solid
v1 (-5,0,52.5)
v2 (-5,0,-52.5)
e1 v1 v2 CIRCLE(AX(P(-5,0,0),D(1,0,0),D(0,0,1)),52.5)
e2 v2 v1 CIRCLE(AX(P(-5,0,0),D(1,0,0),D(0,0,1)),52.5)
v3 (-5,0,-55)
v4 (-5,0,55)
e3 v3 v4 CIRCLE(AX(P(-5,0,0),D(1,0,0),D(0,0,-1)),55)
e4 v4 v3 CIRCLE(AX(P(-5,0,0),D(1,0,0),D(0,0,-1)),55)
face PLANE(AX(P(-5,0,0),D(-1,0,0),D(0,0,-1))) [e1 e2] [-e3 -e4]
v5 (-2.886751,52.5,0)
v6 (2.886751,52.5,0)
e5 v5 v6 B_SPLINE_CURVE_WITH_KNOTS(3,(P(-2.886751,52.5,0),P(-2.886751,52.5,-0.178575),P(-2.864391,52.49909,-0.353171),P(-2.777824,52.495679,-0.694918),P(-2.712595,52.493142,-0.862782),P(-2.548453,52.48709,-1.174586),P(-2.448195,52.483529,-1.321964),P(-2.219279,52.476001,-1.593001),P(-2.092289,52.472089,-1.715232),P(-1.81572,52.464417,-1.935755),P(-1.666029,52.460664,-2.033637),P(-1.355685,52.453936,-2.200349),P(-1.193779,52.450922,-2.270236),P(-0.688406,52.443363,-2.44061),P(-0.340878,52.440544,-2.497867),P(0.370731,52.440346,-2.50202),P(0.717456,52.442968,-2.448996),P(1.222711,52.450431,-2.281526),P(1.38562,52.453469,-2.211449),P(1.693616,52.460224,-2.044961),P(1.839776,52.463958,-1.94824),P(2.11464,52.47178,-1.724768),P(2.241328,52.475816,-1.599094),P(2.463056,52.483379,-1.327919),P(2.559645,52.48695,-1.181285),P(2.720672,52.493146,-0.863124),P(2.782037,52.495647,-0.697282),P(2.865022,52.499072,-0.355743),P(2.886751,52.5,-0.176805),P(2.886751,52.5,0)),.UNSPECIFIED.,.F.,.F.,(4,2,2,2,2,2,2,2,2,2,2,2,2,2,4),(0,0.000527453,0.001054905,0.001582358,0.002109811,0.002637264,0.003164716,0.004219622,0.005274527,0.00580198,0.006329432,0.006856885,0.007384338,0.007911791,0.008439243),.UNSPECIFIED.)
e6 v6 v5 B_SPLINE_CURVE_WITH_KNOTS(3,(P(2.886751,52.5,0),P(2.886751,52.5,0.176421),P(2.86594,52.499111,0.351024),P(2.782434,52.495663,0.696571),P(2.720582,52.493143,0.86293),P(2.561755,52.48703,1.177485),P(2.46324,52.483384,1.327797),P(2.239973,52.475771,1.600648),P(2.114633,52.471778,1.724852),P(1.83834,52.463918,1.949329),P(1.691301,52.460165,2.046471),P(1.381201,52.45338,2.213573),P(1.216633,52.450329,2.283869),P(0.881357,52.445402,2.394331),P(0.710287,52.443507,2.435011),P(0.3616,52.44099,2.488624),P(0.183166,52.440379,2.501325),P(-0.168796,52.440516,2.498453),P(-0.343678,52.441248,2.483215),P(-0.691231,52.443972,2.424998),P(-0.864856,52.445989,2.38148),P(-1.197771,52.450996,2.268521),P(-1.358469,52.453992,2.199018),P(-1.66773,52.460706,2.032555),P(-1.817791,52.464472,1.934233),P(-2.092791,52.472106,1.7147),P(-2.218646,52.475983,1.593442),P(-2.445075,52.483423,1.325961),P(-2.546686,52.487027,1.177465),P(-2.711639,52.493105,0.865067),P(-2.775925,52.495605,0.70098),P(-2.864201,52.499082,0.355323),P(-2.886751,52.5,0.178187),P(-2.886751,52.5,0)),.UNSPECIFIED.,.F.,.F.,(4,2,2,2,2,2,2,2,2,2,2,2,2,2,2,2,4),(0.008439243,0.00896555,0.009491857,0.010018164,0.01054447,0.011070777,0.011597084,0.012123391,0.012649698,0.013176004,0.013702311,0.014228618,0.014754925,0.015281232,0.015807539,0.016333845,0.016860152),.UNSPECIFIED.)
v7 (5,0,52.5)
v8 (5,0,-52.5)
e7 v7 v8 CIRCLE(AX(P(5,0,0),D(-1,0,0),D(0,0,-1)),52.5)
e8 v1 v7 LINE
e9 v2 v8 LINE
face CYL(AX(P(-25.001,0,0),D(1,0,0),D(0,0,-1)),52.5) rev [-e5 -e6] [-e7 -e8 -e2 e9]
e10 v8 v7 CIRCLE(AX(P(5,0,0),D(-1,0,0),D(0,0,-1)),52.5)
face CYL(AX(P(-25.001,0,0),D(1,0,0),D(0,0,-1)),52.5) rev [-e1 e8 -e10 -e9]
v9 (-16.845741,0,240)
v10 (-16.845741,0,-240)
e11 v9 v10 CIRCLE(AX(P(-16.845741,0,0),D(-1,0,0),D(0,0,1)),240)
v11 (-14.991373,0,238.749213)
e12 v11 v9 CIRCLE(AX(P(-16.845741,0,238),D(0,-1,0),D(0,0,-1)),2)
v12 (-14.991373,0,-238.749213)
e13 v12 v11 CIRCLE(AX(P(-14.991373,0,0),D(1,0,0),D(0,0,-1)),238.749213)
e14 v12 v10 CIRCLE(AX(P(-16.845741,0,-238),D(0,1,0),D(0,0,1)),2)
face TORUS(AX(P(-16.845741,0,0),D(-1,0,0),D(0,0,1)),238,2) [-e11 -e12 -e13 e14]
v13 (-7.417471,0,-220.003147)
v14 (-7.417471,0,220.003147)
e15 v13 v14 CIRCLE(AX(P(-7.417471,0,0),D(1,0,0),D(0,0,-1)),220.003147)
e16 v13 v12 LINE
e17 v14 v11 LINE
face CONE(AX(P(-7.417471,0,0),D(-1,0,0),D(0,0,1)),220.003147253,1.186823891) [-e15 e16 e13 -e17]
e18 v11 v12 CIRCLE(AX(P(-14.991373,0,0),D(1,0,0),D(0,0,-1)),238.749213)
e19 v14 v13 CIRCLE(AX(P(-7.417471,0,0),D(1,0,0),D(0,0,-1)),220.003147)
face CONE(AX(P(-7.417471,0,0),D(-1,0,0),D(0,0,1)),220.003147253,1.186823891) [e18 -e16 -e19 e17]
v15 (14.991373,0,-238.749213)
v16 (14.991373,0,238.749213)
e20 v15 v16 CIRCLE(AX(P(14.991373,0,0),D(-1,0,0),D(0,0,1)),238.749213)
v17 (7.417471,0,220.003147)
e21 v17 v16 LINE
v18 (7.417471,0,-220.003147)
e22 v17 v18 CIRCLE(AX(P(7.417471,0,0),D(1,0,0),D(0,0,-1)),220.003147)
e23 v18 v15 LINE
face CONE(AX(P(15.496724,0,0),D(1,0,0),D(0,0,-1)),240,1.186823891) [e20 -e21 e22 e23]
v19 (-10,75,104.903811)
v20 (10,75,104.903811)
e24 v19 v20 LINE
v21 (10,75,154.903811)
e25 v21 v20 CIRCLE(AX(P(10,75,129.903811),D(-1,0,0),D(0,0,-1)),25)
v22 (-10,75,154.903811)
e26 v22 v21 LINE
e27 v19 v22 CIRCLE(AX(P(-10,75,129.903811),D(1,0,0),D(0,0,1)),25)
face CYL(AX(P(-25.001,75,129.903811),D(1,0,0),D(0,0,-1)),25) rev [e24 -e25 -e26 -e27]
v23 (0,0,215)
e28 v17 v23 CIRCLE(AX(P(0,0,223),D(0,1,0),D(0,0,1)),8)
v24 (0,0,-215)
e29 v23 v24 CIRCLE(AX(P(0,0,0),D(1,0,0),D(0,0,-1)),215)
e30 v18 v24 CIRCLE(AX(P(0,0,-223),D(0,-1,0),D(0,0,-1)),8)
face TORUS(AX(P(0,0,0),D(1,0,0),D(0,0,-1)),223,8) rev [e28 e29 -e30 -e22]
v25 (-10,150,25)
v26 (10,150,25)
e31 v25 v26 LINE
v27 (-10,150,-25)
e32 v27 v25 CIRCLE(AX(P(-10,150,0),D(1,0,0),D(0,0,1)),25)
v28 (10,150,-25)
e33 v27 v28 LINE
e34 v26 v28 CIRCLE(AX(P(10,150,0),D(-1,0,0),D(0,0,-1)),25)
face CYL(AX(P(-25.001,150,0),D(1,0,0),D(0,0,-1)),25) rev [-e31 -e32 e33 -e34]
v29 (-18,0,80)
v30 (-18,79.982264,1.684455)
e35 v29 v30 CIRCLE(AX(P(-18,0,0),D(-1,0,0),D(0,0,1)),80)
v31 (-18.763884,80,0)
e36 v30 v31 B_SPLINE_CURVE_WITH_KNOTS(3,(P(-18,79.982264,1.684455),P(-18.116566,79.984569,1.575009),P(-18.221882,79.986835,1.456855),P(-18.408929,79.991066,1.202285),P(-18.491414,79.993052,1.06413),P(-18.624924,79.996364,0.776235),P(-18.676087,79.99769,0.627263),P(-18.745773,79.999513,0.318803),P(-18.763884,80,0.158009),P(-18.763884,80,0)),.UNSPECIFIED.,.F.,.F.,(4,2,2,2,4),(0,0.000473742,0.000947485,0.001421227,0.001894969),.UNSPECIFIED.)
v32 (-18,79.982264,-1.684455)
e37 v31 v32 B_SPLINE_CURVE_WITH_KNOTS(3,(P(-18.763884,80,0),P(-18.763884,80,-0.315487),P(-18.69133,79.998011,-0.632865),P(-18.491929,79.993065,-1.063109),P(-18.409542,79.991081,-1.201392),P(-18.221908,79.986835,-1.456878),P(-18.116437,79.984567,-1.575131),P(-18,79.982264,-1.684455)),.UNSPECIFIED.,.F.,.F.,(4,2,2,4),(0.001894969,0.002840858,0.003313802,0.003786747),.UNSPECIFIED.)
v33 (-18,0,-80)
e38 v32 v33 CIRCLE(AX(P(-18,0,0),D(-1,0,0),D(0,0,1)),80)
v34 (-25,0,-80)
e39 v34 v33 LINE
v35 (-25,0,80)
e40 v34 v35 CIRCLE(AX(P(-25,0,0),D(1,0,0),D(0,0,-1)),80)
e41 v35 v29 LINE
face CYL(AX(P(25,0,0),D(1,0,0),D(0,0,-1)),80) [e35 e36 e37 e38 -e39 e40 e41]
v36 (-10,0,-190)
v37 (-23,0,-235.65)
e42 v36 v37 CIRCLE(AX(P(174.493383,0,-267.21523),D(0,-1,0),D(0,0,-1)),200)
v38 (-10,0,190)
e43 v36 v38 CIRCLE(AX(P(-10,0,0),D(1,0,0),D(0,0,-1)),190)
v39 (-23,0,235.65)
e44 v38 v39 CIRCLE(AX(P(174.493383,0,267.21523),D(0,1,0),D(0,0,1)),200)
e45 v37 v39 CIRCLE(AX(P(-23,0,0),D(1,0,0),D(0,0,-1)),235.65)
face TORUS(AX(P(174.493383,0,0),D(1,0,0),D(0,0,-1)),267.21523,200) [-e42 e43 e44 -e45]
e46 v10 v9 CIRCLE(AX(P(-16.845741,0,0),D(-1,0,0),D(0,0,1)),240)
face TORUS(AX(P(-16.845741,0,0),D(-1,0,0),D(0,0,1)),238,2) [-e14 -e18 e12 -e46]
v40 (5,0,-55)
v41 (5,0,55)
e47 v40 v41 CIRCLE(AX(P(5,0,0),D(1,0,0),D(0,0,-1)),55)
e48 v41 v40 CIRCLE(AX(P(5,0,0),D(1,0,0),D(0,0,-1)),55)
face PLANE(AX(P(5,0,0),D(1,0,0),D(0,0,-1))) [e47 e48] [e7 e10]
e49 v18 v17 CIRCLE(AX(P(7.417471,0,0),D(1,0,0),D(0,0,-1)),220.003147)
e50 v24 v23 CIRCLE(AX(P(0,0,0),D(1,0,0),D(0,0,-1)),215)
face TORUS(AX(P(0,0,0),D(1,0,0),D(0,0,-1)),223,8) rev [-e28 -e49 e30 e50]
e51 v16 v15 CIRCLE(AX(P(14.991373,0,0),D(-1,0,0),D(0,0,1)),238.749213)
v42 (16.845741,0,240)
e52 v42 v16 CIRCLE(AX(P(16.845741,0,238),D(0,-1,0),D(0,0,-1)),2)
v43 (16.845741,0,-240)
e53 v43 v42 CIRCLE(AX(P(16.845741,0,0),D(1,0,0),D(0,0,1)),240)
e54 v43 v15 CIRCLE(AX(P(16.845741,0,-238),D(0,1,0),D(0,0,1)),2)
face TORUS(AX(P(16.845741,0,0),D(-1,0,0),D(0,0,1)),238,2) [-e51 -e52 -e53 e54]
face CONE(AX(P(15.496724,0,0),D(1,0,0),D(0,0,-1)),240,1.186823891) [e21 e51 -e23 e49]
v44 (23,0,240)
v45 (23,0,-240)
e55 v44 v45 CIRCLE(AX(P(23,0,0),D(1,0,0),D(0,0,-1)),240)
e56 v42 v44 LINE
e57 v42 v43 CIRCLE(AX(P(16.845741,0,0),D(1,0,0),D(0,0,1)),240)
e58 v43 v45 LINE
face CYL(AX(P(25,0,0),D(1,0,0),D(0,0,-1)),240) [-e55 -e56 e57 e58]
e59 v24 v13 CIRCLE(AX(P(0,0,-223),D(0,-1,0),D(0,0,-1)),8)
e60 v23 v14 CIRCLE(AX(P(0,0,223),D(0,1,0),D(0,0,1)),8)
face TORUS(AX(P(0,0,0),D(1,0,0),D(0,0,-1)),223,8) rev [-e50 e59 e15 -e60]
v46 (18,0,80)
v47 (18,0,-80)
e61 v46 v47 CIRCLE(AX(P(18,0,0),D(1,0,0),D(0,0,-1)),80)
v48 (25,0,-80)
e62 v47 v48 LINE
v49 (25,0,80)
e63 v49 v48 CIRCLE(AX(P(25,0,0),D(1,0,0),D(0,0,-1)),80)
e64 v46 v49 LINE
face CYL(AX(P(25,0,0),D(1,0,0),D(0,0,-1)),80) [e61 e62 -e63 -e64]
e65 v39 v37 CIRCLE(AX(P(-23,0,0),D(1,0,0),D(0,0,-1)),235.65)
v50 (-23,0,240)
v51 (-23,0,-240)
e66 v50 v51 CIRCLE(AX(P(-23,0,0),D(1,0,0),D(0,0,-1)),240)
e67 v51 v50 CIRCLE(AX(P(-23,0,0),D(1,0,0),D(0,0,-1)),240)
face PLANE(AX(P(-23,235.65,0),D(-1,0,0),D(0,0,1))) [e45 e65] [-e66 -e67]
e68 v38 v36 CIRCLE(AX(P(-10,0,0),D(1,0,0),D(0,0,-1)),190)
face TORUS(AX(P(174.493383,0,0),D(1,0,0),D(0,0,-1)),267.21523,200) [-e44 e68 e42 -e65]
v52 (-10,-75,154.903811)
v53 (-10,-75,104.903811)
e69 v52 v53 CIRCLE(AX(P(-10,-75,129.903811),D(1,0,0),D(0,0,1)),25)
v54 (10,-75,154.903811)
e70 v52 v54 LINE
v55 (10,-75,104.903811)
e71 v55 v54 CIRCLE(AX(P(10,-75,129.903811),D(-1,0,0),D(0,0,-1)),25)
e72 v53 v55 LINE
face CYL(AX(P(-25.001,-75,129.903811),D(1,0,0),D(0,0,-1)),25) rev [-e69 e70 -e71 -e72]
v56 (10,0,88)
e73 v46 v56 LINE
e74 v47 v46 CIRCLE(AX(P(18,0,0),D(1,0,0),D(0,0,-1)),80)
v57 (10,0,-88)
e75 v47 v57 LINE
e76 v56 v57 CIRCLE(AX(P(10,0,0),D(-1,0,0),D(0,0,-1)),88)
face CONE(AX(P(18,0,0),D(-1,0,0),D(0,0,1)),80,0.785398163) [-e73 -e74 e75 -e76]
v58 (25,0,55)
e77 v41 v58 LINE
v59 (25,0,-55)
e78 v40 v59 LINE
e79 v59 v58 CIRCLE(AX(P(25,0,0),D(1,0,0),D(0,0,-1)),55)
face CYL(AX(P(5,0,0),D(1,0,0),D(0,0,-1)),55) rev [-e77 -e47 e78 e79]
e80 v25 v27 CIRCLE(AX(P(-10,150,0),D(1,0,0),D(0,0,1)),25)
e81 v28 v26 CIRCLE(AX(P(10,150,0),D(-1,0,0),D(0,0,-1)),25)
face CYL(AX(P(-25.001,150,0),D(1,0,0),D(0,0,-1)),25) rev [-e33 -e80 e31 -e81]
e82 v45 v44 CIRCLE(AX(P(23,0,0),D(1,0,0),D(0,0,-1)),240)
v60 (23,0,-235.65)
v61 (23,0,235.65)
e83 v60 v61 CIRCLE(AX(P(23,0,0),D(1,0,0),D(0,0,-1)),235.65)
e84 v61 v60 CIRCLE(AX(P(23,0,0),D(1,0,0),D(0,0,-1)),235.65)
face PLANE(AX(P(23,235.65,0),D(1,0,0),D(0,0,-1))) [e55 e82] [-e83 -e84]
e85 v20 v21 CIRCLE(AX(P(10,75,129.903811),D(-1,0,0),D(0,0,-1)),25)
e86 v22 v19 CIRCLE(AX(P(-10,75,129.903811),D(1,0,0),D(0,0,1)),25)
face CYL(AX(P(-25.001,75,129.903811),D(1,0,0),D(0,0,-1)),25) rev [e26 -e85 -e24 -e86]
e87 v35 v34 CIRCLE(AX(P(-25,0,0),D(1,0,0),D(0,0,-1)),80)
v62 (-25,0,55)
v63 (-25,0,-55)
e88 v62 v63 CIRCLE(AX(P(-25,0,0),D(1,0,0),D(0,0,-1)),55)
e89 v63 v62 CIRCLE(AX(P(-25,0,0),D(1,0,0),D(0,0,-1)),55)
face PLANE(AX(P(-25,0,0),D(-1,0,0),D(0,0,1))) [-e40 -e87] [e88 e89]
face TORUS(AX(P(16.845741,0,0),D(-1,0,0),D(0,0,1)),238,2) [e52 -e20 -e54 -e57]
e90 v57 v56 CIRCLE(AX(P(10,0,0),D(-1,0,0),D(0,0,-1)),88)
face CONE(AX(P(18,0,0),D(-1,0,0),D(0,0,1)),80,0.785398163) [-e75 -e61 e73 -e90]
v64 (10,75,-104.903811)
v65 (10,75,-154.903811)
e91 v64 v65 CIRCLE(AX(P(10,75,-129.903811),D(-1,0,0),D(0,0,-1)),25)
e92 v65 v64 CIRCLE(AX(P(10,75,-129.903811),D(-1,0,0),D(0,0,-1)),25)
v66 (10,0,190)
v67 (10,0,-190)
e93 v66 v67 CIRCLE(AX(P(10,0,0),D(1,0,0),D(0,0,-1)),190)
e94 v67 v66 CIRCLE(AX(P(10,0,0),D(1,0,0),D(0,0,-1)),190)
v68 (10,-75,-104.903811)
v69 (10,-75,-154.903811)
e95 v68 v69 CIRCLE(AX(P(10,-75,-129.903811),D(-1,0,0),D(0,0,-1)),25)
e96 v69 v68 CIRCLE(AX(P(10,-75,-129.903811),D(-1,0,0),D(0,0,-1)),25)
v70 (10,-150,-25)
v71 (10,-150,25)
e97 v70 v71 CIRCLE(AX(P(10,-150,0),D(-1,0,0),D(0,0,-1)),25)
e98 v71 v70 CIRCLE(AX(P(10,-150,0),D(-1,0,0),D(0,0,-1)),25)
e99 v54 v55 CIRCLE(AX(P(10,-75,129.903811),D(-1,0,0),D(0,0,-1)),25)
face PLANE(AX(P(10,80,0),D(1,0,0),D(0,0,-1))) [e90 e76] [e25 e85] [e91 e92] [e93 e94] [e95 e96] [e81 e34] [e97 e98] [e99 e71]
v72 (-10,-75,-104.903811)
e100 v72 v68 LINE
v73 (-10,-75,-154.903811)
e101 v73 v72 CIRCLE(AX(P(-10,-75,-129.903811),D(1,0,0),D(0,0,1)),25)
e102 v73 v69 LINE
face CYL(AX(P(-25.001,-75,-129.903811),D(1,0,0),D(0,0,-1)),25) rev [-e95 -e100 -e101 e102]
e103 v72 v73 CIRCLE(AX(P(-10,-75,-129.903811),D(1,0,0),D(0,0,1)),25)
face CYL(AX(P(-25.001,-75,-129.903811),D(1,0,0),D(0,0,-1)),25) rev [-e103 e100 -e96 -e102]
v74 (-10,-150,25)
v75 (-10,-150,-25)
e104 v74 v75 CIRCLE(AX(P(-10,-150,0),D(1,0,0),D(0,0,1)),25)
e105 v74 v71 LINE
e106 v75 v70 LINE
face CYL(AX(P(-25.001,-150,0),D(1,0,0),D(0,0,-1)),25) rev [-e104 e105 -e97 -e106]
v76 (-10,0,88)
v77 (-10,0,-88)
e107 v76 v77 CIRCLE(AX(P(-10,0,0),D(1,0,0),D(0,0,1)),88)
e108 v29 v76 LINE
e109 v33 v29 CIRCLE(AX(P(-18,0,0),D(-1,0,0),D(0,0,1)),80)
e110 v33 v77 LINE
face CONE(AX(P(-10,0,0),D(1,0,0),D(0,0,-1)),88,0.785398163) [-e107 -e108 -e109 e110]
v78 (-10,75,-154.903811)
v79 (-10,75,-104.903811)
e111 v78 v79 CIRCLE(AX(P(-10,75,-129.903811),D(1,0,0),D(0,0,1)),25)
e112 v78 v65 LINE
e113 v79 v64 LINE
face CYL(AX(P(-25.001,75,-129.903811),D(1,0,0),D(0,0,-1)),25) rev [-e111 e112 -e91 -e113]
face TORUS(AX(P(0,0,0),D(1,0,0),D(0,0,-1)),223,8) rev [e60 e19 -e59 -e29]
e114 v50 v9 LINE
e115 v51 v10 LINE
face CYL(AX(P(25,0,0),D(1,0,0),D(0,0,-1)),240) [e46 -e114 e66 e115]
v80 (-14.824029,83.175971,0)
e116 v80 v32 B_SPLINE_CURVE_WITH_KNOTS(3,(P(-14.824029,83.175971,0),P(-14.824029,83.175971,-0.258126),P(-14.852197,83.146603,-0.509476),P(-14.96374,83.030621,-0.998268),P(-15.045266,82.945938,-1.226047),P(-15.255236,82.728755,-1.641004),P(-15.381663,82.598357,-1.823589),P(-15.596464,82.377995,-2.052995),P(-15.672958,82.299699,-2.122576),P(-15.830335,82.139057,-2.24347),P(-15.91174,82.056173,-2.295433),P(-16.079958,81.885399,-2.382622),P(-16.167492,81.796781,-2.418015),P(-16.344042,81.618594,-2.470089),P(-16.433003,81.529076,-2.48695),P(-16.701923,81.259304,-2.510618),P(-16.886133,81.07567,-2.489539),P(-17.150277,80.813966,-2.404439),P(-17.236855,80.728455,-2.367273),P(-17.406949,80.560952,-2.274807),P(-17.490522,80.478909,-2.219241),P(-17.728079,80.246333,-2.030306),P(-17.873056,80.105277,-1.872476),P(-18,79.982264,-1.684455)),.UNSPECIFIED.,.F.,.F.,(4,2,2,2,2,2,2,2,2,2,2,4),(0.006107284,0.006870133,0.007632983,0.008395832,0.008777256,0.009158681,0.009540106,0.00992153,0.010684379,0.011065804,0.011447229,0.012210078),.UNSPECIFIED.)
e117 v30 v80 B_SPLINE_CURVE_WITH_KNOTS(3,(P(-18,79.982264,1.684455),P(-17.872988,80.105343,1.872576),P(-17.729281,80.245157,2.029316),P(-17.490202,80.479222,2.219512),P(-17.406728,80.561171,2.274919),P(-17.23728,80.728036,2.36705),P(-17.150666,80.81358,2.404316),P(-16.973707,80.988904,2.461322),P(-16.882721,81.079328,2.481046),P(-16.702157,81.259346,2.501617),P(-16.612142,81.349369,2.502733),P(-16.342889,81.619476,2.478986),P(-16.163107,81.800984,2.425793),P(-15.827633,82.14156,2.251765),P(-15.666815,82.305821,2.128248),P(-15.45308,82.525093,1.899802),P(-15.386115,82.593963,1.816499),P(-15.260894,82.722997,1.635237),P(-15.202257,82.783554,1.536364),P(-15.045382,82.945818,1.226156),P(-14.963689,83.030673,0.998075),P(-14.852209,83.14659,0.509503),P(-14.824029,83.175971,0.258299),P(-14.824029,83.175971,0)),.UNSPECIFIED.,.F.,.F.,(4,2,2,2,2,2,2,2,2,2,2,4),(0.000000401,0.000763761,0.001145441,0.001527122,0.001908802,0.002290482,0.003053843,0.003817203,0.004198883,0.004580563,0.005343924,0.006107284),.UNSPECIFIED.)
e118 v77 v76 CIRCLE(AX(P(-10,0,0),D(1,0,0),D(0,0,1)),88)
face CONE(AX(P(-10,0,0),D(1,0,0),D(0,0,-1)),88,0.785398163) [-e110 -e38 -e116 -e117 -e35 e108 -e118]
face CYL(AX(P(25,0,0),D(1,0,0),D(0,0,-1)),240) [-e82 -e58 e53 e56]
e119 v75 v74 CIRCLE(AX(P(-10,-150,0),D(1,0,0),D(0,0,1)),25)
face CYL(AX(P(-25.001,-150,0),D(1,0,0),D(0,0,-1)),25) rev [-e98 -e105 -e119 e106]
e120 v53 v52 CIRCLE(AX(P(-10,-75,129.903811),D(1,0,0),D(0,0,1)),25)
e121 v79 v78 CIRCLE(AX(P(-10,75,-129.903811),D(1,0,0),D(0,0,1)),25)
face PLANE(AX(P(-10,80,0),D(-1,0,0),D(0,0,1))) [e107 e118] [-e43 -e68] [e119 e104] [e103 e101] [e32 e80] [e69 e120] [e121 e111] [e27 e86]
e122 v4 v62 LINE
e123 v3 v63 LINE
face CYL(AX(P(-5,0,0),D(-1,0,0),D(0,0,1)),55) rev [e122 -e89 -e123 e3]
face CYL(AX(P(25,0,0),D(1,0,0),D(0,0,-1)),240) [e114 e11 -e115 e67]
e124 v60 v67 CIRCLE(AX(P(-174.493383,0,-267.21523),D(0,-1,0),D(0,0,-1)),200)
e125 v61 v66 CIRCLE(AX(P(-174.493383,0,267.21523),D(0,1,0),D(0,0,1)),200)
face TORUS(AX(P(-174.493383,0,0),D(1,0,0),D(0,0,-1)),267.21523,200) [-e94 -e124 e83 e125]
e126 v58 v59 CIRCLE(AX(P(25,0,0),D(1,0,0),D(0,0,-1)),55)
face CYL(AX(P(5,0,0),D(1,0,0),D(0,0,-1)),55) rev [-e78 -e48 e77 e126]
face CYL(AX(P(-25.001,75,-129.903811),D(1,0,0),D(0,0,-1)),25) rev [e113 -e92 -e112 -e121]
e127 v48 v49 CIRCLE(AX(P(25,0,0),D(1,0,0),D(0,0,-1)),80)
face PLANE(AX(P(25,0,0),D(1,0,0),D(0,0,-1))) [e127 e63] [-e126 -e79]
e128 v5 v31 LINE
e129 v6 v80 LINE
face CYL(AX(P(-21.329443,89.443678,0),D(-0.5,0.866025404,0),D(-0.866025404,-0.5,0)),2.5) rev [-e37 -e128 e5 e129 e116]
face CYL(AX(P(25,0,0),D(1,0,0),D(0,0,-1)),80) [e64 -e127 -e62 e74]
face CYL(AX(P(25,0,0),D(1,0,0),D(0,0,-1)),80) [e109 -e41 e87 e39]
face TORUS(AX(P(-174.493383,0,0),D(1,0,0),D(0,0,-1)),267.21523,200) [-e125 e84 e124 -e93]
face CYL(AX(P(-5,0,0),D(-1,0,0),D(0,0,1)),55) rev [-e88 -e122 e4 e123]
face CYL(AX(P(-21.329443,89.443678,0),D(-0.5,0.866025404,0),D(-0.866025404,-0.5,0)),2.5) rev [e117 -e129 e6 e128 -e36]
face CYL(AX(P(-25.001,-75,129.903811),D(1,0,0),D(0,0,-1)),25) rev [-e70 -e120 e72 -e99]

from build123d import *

# Parameters (mm, degrees)
CUT_EXTRUDE1_REACH = 345.074
SKETCH2_R          = 52.5
SKETCH2_R_2        = 25
SKETCH4_R          = 55
CUT_EXTRUDE2_DEPTH = 20
CHAMFER1_SIZE      = 8
FILLET1_R          = 2


with BuildPart() as part:
    # Sketch1 → Revolve1 (revolve)
    with BuildSketch(Plane.XY, mode=Mode.PRIVATE) as revolve1_sk:
        with BuildLine():
            Line((25, 0), (25, 80))
            Line((25, 80), (10, 80))
            Line((10, 80), (10, 190))
            ThreePointArc((10, 190), (17.859035688, 212.437979979), (23, 235.65))
            Line((23, 235.65), (23, 240))
            Line((23, 240), (15.496723781, 240))
            Line((15.496723781, 240), (7.417470837, 220.003147253))
            ThreePointArc((7.417470837, 220.003147253), (0, 215), (-7.417470837, 220.003147253))
            Line((-7.417470837, 220.003147253), (-15.496723781, 240))
            Line((-15.496723781, 240), (-23, 240))
            Line((-23, 240), (-23, 235.65))
            ThreePointArc((-23, 235.65), (-17.859035688, 212.437979979), (-10, 190))
            Line((-10, 190), (-10, 80))
            Line((-10, 80), (-25, 80))
            Line((-25, 80), (-25, 0))
            Line((-25, 0), (25, 0))
        make_face()
    revolve(revolve1_sk.sketch.rotate(Axis((25, 0, 0), (-1, 0, 0)), 90), axis=Axis((25, 0, 0), (-1, 0, 0)))

    # Sketch2 → Cut-Extrude1 (cut, up to next)
    with BuildSketch(Plane(origin=(25, 0, 0), x_dir=(0, 0, -1), z_dir=(1, 0, 0)), mode=Mode.PRIVATE) as cut_extrude1_sk1:
        Circle(SKETCH2_R)
    cut_extrude1_tool1 = extrude(cut_extrude1_sk1.sketch, amount=-CUT_EXTRUDE1_REACH, mode=Mode.PRIVATE) & part.part
    # Sketch2 → Cut-Extrude1 (cut, up to next)
    with BuildSketch(Plane(origin=(25, 0, 0), x_dir=(0, 0, -1), z_dir=(1, 0, 0)), mode=Mode.PRIVATE) as cut_extrude1_sk2:
        with Locations((0, 150)):
            Circle(SKETCH2_R_2)
    cut_extrude1_tool2 = extrude(cut_extrude1_sk2.sketch, amount=-CUT_EXTRUDE1_REACH, mode=Mode.PRIVATE) & part.part
    # Sketch2 → Cut-Extrude1 (cut, up to next)
    with BuildSketch(Plane(origin=(25, 0, 0), x_dir=(0, 0, -1), z_dir=(1, 0, 0)), mode=Mode.PRIVATE) as cut_extrude1_sk3:
        with Locations((129.903810568, 75)):
            Circle(SKETCH2_R_2)
    cut_extrude1_tool3 = extrude(cut_extrude1_sk3.sketch, amount=-CUT_EXTRUDE1_REACH, mode=Mode.PRIVATE) & part.part
    # Sketch2 → Cut-Extrude1 (cut, up to next)
    with BuildSketch(Plane(origin=(25, 0, 0), x_dir=(0, 0, -1), z_dir=(1, 0, 0)), mode=Mode.PRIVATE) as cut_extrude1_sk4:
        with Locations((129.903810568, -75)):
            Circle(SKETCH2_R_2)
    cut_extrude1_tool4 = extrude(cut_extrude1_sk4.sketch, amount=-CUT_EXTRUDE1_REACH, mode=Mode.PRIVATE) & part.part
    # Sketch2 → Cut-Extrude1 (cut, up to next)
    with BuildSketch(Plane(origin=(25, 0, 0), x_dir=(0, 0, -1), z_dir=(1, 0, 0)), mode=Mode.PRIVATE) as cut_extrude1_sk5:
        with Locations((0, -150)):
            Circle(SKETCH2_R_2)
    cut_extrude1_tool5 = extrude(cut_extrude1_sk5.sketch, amount=-CUT_EXTRUDE1_REACH, mode=Mode.PRIVATE) & part.part
    # Sketch2 → Cut-Extrude1 (cut, up to next)
    with BuildSketch(Plane(origin=(25, 0, 0), x_dir=(0, 0, -1), z_dir=(1, 0, 0)), mode=Mode.PRIVATE) as cut_extrude1_sk6:
        with Locations((-129.903810568, -75)):
            Circle(SKETCH2_R_2)
    cut_extrude1_tool6 = extrude(cut_extrude1_sk6.sketch, amount=-CUT_EXTRUDE1_REACH, mode=Mode.PRIVATE) & part.part
    # Sketch2 → Cut-Extrude1 (cut, up to next)
    with BuildSketch(Plane(origin=(25, 0, 0), x_dir=(0, 0, -1), z_dir=(1, 0, 0)), mode=Mode.PRIVATE) as cut_extrude1_sk7:
        with Locations((-129.903810568, 75)):
            Circle(SKETCH2_R_2)
    cut_extrude1_tool7 = extrude(cut_extrude1_sk7.sketch, amount=-CUT_EXTRUDE1_REACH, mode=Mode.PRIVATE) & part.part
    add(cut_extrude1_tool1.solids().sort_by_distance((25, 0, 0))[0], mode=Mode.SUBTRACT)
    add(cut_extrude1_tool2.solids().sort_by_distance((25, 150, 0))[0], mode=Mode.SUBTRACT)
    add(cut_extrude1_tool3.solids().sort_by_distance((25, 75, -129.903811))[0], mode=Mode.SUBTRACT)
    add(cut_extrude1_tool4.solids().sort_by_distance((25, -75, -129.903811))[0], mode=Mode.SUBTRACT)
    add(cut_extrude1_tool5.solids().sort_by_distance((25, -150, 0))[0], mode=Mode.SUBTRACT)
    add(cut_extrude1_tool6.solids().sort_by_distance((25, -75, 129.903811))[0], mode=Mode.SUBTRACT)
    add(cut_extrude1_tool7.solids().sort_by_distance((25, 75, 129.903811))[0], mode=Mode.SUBTRACT)

    # Sketch4 → Cut-Extrude2 (cut)
    with BuildSketch(Plane(origin=(25, 0, 0), x_dir=(0, 0, -1), z_dir=(1, 0, 0))):
        Circle(SKETCH4_R)
    cut_extrude2 = extrude(amount=-CUT_EXTRUDE2_DEPTH, mode=Mode.SUBTRACT)

    # Mirror1: Cut-Extrude2 across plane
    add(cut_extrude2.mirror(Plane(origin=(0, 0, 0), x_dir=(0, 0, 1), z_dir=(1, 0, 0))), mode=Mode.SUBTRACT)

    # Chamfer1
    chamfer1_edges = [part.edges().sort_by_distance(p)[0] for p in [
        (10, 0, 80),
        (-10, 0, 80),
    ]]
    chamfer(chamfer1_edges, length=CHAMFER1_SIZE)

    # Sketch6 → Cut-Revolve1 (revolve, cut)
    with BuildSketch(Plane.XY, mode=Mode.PRIVATE) as cut_revolve1_sk:
        Polygon((-21.329442598, 89.443678278), (3.094493481, 47.140180068), (5.25955699, 48.390180068), (-19.164379089, 90.693678278), align=None)
    revolve(cut_revolve1_sk.sketch.rotate(Axis((-21.329442598, 89.443678278, 0), (0.49999999999999506, -0.8660254037844416, 0)), 180), axis=Axis((-21.329442598, 89.443678278, 0), (0.49999999999999506, -0.8660254037844416, 0)), mode=Mode.SUBTRACT)

    # Fillet1
    fillet1_edges = [part.edges().sort_by_distance(p)[0] for p in [
        (15.496723781, 0, 240),
        (-15.496723781, 0, 240),
    ]]
    fillet(fillet1_edges, radius=FILLET1_R)


solid = part.part
